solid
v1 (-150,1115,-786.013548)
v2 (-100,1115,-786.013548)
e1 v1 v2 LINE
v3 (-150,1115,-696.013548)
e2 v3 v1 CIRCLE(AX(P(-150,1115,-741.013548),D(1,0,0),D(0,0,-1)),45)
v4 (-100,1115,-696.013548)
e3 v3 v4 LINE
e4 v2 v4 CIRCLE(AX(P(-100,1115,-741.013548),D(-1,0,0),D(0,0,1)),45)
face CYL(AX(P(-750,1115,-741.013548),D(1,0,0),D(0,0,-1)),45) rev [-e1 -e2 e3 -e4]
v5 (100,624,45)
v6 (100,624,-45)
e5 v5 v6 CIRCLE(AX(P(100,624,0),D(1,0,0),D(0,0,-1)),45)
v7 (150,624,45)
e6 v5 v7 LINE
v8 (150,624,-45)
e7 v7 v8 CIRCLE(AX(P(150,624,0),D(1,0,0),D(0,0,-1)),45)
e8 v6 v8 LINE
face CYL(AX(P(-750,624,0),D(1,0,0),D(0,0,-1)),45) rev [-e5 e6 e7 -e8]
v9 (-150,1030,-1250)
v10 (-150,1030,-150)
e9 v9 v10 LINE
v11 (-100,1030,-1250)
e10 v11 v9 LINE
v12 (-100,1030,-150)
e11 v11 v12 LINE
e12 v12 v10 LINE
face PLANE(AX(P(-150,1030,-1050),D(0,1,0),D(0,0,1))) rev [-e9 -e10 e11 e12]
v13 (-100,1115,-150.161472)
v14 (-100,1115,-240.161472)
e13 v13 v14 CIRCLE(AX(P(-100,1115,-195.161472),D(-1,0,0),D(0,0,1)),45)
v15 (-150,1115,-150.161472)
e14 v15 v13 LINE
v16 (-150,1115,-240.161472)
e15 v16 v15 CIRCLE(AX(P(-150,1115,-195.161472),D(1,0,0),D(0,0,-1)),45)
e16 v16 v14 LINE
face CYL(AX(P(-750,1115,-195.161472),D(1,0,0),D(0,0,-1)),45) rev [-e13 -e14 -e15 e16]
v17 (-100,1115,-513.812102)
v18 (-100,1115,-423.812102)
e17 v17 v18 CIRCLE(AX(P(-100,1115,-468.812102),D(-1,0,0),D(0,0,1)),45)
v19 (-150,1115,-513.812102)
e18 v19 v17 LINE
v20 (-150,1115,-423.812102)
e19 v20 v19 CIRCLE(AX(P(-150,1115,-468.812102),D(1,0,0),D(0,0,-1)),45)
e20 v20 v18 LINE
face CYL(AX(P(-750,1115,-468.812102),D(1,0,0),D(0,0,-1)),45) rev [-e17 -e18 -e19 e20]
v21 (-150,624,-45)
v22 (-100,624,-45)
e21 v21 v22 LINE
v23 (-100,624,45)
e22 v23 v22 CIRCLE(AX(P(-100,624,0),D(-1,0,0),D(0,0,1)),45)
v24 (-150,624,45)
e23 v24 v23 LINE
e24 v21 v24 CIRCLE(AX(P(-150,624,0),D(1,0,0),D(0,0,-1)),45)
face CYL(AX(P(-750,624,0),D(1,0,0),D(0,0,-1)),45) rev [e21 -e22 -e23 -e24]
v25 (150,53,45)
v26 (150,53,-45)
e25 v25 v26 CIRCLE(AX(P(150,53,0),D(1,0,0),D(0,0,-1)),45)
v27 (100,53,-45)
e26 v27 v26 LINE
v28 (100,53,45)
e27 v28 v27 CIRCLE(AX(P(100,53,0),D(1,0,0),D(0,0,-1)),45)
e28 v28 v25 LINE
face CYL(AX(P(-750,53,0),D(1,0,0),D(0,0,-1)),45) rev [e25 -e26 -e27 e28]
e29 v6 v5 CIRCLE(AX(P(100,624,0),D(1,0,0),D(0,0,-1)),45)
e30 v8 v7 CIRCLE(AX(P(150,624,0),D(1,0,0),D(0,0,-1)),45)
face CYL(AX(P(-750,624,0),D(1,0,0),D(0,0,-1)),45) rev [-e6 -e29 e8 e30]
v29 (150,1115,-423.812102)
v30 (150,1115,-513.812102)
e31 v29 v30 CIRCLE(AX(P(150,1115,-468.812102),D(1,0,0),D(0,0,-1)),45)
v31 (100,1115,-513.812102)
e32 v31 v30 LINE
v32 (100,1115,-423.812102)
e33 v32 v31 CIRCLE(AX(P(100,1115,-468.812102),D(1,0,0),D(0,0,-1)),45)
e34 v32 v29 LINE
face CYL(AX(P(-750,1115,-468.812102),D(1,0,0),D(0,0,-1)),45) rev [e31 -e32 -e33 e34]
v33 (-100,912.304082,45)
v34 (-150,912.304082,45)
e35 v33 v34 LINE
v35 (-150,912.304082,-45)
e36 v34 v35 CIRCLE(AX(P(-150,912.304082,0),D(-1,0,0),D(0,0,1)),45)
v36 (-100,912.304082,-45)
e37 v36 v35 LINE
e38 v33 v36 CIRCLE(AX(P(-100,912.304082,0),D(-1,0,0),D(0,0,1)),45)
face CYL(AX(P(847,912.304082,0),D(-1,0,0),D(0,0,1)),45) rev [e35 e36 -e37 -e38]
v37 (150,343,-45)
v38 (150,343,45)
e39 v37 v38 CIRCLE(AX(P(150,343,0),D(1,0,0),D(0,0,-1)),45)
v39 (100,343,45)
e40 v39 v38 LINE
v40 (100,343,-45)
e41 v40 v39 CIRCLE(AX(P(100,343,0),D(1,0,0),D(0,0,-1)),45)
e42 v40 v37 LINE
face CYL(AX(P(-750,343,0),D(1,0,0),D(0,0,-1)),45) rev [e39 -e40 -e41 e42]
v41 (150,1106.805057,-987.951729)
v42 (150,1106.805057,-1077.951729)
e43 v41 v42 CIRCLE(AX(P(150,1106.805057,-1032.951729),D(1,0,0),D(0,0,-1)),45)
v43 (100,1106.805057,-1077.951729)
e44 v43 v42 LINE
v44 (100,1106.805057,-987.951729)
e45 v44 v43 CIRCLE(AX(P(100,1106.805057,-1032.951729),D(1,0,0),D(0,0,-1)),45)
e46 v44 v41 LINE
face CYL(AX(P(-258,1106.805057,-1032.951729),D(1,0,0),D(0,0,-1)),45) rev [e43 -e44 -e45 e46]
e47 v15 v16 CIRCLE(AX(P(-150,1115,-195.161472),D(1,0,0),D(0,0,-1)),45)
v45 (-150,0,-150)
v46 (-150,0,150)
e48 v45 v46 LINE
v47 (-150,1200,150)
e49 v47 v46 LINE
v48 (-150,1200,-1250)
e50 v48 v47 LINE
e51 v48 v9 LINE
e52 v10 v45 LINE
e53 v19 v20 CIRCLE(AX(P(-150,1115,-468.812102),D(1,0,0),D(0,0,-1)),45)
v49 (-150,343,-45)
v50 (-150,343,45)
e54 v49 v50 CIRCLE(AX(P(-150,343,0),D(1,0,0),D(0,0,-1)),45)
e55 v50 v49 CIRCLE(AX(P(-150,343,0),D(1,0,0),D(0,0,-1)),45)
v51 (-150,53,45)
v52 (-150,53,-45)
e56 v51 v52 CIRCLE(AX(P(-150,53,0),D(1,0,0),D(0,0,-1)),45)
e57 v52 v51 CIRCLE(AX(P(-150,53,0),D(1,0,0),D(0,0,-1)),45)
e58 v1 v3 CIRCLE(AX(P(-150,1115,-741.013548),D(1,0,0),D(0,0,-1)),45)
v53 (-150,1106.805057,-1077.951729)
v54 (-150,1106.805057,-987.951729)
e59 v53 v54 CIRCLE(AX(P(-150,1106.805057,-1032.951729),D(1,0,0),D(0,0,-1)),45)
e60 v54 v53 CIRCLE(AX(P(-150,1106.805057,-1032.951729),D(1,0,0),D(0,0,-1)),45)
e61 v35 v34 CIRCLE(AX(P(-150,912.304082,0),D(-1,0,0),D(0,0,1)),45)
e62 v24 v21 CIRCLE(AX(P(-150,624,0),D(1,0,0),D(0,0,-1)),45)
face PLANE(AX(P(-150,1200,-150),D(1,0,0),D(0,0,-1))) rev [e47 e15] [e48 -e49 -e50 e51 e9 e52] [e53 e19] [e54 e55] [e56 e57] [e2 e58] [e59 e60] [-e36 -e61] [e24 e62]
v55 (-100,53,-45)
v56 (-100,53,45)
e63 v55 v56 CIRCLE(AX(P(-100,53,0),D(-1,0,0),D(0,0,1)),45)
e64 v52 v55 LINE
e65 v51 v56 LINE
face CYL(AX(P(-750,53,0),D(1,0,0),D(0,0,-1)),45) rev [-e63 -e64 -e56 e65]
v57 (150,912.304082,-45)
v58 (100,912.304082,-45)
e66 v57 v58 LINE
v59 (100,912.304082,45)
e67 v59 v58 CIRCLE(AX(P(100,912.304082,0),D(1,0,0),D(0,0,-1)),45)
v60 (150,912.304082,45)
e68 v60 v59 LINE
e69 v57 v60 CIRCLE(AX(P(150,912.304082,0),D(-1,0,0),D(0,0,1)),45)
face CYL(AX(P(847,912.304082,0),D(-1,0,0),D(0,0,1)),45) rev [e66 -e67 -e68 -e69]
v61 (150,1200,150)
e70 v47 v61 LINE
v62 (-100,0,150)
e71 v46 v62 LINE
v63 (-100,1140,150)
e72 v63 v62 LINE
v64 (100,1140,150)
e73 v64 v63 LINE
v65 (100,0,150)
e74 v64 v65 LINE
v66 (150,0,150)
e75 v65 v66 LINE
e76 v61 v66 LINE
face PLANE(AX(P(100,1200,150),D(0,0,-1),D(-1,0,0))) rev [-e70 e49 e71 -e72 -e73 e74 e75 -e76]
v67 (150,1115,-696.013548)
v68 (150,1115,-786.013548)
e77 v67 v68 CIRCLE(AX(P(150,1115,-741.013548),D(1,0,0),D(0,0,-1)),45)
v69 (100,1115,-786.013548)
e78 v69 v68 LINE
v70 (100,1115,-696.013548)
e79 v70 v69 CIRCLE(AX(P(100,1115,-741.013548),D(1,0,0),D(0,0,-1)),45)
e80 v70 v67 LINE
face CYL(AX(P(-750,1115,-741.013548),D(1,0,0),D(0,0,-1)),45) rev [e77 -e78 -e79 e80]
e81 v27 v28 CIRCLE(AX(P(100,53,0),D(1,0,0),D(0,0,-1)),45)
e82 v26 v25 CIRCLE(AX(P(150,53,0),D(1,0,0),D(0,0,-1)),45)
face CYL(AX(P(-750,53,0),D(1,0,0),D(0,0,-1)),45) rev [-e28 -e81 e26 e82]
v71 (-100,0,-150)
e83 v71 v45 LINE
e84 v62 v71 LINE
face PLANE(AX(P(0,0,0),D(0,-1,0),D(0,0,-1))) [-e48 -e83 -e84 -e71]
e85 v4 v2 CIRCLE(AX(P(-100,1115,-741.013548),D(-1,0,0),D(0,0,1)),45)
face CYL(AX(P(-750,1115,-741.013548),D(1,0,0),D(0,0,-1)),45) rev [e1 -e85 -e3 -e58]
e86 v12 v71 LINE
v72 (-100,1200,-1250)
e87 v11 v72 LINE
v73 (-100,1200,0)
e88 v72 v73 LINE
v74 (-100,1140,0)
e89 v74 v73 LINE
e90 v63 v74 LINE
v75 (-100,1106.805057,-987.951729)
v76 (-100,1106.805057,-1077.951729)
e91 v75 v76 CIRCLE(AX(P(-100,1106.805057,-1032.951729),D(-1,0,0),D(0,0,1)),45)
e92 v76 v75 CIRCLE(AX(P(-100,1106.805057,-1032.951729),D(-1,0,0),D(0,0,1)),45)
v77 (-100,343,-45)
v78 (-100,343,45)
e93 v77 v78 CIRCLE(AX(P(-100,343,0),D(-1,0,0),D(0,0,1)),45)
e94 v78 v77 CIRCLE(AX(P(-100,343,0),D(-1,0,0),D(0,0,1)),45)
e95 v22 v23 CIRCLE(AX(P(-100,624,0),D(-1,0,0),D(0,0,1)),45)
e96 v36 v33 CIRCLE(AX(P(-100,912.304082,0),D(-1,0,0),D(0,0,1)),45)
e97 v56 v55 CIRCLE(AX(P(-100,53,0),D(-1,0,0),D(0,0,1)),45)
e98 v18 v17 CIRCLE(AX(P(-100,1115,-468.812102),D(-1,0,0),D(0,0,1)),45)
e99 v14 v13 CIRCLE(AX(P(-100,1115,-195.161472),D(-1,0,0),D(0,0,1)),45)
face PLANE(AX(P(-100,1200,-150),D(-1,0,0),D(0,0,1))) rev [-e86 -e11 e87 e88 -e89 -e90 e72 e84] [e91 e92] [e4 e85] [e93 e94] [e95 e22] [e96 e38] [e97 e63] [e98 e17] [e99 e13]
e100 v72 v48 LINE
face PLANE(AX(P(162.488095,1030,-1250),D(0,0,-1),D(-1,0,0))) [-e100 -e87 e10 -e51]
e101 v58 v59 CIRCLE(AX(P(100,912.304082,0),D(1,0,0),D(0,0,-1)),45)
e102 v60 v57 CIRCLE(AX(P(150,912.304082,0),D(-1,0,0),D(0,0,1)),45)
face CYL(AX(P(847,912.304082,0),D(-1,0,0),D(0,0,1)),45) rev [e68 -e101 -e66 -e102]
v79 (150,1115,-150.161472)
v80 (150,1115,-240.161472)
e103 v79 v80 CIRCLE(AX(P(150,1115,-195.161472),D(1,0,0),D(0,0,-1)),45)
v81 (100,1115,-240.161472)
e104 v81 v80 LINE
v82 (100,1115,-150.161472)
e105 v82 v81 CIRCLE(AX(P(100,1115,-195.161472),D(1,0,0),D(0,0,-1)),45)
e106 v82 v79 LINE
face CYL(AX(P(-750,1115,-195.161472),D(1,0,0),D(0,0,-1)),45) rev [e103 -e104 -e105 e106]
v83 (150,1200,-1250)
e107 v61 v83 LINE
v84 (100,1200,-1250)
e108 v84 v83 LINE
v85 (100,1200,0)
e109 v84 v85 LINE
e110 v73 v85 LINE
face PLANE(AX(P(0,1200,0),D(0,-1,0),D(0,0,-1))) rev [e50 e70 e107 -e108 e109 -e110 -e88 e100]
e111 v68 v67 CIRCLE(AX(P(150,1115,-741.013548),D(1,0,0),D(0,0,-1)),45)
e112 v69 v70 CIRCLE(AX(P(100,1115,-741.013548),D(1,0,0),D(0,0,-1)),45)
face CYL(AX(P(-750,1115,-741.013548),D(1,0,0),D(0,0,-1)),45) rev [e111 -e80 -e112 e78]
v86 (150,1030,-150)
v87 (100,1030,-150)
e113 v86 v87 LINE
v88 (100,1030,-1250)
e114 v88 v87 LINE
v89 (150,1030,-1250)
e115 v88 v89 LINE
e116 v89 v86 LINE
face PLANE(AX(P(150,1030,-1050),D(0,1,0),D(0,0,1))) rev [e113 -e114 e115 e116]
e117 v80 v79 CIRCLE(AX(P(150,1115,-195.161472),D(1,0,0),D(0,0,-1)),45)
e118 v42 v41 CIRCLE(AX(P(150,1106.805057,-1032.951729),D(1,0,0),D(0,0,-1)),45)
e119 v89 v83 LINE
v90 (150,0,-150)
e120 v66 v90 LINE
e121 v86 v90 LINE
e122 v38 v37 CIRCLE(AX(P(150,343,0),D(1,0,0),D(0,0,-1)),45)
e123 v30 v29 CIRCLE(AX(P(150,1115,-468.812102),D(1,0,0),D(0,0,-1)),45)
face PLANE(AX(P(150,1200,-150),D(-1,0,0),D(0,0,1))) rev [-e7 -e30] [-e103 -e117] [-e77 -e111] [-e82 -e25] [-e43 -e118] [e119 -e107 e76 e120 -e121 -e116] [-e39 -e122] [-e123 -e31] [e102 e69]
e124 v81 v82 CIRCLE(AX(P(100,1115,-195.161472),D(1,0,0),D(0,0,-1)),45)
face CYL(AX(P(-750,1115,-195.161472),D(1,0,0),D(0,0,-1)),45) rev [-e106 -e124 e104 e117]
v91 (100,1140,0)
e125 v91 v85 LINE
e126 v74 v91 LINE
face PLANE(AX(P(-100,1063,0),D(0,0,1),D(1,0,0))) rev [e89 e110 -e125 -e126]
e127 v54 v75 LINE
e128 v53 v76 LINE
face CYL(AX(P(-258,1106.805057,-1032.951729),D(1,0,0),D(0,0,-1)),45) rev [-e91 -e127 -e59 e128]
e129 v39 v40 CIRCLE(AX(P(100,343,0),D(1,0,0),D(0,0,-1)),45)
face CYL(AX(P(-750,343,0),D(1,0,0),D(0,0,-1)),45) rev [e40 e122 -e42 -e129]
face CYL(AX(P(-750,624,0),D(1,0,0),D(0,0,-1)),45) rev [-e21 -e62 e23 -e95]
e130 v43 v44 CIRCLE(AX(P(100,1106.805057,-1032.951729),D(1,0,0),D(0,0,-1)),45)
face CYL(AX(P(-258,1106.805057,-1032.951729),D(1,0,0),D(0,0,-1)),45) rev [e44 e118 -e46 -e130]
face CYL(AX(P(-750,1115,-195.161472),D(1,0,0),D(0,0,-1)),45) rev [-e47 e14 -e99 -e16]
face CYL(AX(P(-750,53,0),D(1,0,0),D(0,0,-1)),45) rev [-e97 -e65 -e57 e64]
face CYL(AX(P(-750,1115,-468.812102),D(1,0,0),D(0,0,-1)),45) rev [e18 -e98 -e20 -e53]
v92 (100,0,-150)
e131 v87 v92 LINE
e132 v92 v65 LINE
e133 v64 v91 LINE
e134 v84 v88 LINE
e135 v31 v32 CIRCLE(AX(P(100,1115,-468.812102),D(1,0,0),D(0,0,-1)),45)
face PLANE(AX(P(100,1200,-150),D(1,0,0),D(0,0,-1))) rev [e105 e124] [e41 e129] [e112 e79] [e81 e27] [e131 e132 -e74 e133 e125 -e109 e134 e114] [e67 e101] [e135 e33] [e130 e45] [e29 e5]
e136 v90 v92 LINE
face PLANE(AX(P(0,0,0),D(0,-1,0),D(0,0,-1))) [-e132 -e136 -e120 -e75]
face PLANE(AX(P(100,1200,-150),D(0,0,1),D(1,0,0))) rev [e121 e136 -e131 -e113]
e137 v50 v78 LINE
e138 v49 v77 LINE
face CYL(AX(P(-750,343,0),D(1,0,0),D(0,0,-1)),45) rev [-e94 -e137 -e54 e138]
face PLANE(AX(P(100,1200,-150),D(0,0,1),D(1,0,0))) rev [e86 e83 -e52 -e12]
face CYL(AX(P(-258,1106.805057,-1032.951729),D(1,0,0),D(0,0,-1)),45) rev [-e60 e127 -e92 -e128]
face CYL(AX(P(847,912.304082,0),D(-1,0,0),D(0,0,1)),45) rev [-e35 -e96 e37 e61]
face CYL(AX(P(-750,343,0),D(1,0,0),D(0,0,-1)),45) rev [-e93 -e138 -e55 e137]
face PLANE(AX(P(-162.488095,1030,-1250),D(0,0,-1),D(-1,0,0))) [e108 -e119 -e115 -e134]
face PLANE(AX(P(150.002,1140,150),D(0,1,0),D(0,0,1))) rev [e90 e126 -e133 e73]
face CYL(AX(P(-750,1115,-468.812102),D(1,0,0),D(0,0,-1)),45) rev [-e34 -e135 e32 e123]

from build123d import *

# Parameters (mm, degrees)
SKETCH1_W             = 50
SKETCH1_H             = 300
BOSS_EXTRUDE1_DEPTH   = 1200
BOSS_EXTRUDE1_2_DEPTH = 1200
BOSS_EXTRUDE2_REACH   = 1236.909
SKETCH2_W             = 300
SKETCH2_H             = 60
SKETCH3_R             = 45
CUT_EXTRUDE1_DEPTH    = 900
SKETCH5_W             = 50
SKETCH5_H             = 170
BOSS_EXTRUDE3_DEPTH   = 900
SKETCH7_R             = 45
CUT_EXTRUDE2_DEPTH    = 900
SKETCH8_W             = 200
SKETCH8_H             = 150
CUT_EXTRUDE3_DEPTH    = 137
SKETCH9_R             = 45.000000002
CUT_EXTRUDE4_DEPTH    = 408
SKETCH10_R            = 45
CUT_EXTRUDE5_DEPTH    = 997
BOSS_EXTRUDE4_START   = -50
BOSS_EXTRUDE4_DEPTH   = 50
BOSS_EXTRUDE5_DEPTH   = 50


with BuildPart() as part:
    # Sketch1 → Boss-Extrude1 (new body)
    with BuildSketch(Plane(origin=(0, 0, 0), x_dir=(1, 0, 0), z_dir=(0, 1, 0))):
        with Locations((125, 0)):
            Rectangle(SKETCH1_W, SKETCH1_H)
    extrude(amount=BOSS_EXTRUDE1_DEPTH)

    # Sketch2 → Boss-Extrude2 (add, up to next)
    with BuildSketch(Plane(origin=(-100, 0, 0), x_dir=(0, 0, -1), z_dir=(1, 0, 0)), mode=Mode.PRIVATE) as boss_extrude2_sk1:
        with Locations((0, 1170)):
            Rectangle(SKETCH2_W, SKETCH2_H)
    boss_extrude2_tool1 = extrude(boss_extrude2_sk1.sketch, amount=BOSS_EXTRUDE2_REACH, mode=Mode.PRIVATE) - part.part


with BuildPart() as body_2:
    # Sketch1 → Boss-Extrude1 2 (new body)
    with BuildSketch(Plane(origin=(0, 0, 0), x_dir=(1, 0, 0), z_dir=(0, 1, 0))):
        with Locations((-125, 0)):
            Rectangle(SKETCH1_W, SKETCH1_H)
    extrude(amount=BOSS_EXTRUDE1_2_DEPTH)


with BuildPart() as part_1:
    add(part.part)

    add(body_2.part)  # Boss-Extrude2 merges body 2
    add(boss_extrude2_tool1.solids().sort_by_distance((-100, 1170, 0))[0])

    # Sketch3 → Cut-Extrude1 (cut)
    with BuildSketch(Plane(origin=(150, 0, 0), x_dir=(0, 0, -1), z_dir=(1, 0, 0))):
        with Locations((0, 624)):
            Circle(SKETCH3_R)
        with Locations((0, 343)):
            Circle(SKETCH3_R)
        with Locations((0, 53)):
            Circle(SKETCH3_R)
    extrude(amount=-CUT_EXTRUDE1_DEPTH, mode=Mode.SUBTRACT)

    # Sketch5 → Boss-Extrude3 (add)
    with BuildSketch(Plane(origin=(0, 0, -150), x_dir=(-1, 0, 0), z_dir=(0, 0, -1))):
        with Locations((-125, 1115)):
            Rectangle(SKETCH5_W, SKETCH5_H)
        with Locations((125, 1115)):
            Rectangle(SKETCH5_W, SKETCH5_H)
    extrude(amount=BOSS_EXTRUDE3_DEPTH)

    # Sketch7 → Cut-Extrude2 (cut)
    with BuildSketch(Plane(origin=(150, 0, 0), x_dir=(0, 0, -1), z_dir=(1, 0, 0))):
        with Locations((468.812102097, 1115)):
            Circle(SKETCH7_R)
        with Locations((741.013548247, 1115)):
            Circle(SKETCH7_R)
        with Locations((195.161471607, 1115)):
            Circle(SKETCH7_R)
    extrude(amount=-CUT_EXTRUDE2_DEPTH, mode=Mode.SUBTRACT)

    # Sketch8 → Cut-Extrude3 (cut)
    with BuildSketch(Plane(origin=(0, 1200, 0), x_dir=(1, 0, 0), z_dir=(0, 1, 0))):
        with Locations((0, 75)):
            Rectangle(SKETCH8_W, SKETCH8_H)
    extrude(amount=-CUT_EXTRUDE3_DEPTH, mode=Mode.SUBTRACT)

    # Sketch9 → Cut-Extrude4 (cut)
    with BuildSketch(Plane(origin=(150, 0, 0), x_dir=(0, 0, -1), z_dir=(1, 0, 0))):
        with Locations((1032.951729484, 1106.805056962)):
            Circle(SKETCH9_R)
    extrude(amount=-CUT_EXTRUDE4_DEPTH, mode=Mode.SUBTRACT)

    # Sketch10 → Cut-Extrude5 (cut)
    with BuildSketch(Plane.ZY.offset(150)):
        with Locations((0, 912.304081816)):
            Circle(SKETCH10_R)
    extrude(amount=-CUT_EXTRUDE5_DEPTH, mode=Mode.SUBTRACT)

    # Sketch12 → Boss-Extrude4 (add)
    with BuildSketch(Plane.ZY.offset(150).offset(BOSS_EXTRUDE4_START)):
        with BuildLine():
            Line((-1050, 1200), (-1250, 1200))
            Line((-1250, 1200), (-1250, 1030))
            Line((-1250, 1030), (-1050, 1030))
            Line((-1050, 1030), (-1050, 1065.159451282))
            ThreePointArc((-1050, 1065.159451282), (-1077.951729484, 1106.805056962), (-1050, 1148.450662641))
            Line((-1050, 1148.450662641), (-1050, 1200))
        make_face()
    extrude(amount=BOSS_EXTRUDE4_DEPTH)

    # Sketch13 → Boss-Extrude5 (add)
    with BuildSketch(Plane(origin=(150, 0, 0), x_dir=(0, 0, -1), z_dir=(1, 0, 0))):
        with BuildLine():
            Line((1250, 1200), (1050, 1200))
            Line((1050, 1200), (1050, 1148.450662641))
            ThreePointArc((1050, 1148.450662641), (1077.951729484, 1106.805056962), (1050, 1065.159451282))
            Line((1050, 1065.159451282), (1050, 1030))
            Line((1050, 1030), (1250, 1030))
            Line((1250, 1030), (1250, 1200))
        make_face()
    extrude(amount=-BOSS_EXTRUDE5_DEPTH)


solid = part_1.part
